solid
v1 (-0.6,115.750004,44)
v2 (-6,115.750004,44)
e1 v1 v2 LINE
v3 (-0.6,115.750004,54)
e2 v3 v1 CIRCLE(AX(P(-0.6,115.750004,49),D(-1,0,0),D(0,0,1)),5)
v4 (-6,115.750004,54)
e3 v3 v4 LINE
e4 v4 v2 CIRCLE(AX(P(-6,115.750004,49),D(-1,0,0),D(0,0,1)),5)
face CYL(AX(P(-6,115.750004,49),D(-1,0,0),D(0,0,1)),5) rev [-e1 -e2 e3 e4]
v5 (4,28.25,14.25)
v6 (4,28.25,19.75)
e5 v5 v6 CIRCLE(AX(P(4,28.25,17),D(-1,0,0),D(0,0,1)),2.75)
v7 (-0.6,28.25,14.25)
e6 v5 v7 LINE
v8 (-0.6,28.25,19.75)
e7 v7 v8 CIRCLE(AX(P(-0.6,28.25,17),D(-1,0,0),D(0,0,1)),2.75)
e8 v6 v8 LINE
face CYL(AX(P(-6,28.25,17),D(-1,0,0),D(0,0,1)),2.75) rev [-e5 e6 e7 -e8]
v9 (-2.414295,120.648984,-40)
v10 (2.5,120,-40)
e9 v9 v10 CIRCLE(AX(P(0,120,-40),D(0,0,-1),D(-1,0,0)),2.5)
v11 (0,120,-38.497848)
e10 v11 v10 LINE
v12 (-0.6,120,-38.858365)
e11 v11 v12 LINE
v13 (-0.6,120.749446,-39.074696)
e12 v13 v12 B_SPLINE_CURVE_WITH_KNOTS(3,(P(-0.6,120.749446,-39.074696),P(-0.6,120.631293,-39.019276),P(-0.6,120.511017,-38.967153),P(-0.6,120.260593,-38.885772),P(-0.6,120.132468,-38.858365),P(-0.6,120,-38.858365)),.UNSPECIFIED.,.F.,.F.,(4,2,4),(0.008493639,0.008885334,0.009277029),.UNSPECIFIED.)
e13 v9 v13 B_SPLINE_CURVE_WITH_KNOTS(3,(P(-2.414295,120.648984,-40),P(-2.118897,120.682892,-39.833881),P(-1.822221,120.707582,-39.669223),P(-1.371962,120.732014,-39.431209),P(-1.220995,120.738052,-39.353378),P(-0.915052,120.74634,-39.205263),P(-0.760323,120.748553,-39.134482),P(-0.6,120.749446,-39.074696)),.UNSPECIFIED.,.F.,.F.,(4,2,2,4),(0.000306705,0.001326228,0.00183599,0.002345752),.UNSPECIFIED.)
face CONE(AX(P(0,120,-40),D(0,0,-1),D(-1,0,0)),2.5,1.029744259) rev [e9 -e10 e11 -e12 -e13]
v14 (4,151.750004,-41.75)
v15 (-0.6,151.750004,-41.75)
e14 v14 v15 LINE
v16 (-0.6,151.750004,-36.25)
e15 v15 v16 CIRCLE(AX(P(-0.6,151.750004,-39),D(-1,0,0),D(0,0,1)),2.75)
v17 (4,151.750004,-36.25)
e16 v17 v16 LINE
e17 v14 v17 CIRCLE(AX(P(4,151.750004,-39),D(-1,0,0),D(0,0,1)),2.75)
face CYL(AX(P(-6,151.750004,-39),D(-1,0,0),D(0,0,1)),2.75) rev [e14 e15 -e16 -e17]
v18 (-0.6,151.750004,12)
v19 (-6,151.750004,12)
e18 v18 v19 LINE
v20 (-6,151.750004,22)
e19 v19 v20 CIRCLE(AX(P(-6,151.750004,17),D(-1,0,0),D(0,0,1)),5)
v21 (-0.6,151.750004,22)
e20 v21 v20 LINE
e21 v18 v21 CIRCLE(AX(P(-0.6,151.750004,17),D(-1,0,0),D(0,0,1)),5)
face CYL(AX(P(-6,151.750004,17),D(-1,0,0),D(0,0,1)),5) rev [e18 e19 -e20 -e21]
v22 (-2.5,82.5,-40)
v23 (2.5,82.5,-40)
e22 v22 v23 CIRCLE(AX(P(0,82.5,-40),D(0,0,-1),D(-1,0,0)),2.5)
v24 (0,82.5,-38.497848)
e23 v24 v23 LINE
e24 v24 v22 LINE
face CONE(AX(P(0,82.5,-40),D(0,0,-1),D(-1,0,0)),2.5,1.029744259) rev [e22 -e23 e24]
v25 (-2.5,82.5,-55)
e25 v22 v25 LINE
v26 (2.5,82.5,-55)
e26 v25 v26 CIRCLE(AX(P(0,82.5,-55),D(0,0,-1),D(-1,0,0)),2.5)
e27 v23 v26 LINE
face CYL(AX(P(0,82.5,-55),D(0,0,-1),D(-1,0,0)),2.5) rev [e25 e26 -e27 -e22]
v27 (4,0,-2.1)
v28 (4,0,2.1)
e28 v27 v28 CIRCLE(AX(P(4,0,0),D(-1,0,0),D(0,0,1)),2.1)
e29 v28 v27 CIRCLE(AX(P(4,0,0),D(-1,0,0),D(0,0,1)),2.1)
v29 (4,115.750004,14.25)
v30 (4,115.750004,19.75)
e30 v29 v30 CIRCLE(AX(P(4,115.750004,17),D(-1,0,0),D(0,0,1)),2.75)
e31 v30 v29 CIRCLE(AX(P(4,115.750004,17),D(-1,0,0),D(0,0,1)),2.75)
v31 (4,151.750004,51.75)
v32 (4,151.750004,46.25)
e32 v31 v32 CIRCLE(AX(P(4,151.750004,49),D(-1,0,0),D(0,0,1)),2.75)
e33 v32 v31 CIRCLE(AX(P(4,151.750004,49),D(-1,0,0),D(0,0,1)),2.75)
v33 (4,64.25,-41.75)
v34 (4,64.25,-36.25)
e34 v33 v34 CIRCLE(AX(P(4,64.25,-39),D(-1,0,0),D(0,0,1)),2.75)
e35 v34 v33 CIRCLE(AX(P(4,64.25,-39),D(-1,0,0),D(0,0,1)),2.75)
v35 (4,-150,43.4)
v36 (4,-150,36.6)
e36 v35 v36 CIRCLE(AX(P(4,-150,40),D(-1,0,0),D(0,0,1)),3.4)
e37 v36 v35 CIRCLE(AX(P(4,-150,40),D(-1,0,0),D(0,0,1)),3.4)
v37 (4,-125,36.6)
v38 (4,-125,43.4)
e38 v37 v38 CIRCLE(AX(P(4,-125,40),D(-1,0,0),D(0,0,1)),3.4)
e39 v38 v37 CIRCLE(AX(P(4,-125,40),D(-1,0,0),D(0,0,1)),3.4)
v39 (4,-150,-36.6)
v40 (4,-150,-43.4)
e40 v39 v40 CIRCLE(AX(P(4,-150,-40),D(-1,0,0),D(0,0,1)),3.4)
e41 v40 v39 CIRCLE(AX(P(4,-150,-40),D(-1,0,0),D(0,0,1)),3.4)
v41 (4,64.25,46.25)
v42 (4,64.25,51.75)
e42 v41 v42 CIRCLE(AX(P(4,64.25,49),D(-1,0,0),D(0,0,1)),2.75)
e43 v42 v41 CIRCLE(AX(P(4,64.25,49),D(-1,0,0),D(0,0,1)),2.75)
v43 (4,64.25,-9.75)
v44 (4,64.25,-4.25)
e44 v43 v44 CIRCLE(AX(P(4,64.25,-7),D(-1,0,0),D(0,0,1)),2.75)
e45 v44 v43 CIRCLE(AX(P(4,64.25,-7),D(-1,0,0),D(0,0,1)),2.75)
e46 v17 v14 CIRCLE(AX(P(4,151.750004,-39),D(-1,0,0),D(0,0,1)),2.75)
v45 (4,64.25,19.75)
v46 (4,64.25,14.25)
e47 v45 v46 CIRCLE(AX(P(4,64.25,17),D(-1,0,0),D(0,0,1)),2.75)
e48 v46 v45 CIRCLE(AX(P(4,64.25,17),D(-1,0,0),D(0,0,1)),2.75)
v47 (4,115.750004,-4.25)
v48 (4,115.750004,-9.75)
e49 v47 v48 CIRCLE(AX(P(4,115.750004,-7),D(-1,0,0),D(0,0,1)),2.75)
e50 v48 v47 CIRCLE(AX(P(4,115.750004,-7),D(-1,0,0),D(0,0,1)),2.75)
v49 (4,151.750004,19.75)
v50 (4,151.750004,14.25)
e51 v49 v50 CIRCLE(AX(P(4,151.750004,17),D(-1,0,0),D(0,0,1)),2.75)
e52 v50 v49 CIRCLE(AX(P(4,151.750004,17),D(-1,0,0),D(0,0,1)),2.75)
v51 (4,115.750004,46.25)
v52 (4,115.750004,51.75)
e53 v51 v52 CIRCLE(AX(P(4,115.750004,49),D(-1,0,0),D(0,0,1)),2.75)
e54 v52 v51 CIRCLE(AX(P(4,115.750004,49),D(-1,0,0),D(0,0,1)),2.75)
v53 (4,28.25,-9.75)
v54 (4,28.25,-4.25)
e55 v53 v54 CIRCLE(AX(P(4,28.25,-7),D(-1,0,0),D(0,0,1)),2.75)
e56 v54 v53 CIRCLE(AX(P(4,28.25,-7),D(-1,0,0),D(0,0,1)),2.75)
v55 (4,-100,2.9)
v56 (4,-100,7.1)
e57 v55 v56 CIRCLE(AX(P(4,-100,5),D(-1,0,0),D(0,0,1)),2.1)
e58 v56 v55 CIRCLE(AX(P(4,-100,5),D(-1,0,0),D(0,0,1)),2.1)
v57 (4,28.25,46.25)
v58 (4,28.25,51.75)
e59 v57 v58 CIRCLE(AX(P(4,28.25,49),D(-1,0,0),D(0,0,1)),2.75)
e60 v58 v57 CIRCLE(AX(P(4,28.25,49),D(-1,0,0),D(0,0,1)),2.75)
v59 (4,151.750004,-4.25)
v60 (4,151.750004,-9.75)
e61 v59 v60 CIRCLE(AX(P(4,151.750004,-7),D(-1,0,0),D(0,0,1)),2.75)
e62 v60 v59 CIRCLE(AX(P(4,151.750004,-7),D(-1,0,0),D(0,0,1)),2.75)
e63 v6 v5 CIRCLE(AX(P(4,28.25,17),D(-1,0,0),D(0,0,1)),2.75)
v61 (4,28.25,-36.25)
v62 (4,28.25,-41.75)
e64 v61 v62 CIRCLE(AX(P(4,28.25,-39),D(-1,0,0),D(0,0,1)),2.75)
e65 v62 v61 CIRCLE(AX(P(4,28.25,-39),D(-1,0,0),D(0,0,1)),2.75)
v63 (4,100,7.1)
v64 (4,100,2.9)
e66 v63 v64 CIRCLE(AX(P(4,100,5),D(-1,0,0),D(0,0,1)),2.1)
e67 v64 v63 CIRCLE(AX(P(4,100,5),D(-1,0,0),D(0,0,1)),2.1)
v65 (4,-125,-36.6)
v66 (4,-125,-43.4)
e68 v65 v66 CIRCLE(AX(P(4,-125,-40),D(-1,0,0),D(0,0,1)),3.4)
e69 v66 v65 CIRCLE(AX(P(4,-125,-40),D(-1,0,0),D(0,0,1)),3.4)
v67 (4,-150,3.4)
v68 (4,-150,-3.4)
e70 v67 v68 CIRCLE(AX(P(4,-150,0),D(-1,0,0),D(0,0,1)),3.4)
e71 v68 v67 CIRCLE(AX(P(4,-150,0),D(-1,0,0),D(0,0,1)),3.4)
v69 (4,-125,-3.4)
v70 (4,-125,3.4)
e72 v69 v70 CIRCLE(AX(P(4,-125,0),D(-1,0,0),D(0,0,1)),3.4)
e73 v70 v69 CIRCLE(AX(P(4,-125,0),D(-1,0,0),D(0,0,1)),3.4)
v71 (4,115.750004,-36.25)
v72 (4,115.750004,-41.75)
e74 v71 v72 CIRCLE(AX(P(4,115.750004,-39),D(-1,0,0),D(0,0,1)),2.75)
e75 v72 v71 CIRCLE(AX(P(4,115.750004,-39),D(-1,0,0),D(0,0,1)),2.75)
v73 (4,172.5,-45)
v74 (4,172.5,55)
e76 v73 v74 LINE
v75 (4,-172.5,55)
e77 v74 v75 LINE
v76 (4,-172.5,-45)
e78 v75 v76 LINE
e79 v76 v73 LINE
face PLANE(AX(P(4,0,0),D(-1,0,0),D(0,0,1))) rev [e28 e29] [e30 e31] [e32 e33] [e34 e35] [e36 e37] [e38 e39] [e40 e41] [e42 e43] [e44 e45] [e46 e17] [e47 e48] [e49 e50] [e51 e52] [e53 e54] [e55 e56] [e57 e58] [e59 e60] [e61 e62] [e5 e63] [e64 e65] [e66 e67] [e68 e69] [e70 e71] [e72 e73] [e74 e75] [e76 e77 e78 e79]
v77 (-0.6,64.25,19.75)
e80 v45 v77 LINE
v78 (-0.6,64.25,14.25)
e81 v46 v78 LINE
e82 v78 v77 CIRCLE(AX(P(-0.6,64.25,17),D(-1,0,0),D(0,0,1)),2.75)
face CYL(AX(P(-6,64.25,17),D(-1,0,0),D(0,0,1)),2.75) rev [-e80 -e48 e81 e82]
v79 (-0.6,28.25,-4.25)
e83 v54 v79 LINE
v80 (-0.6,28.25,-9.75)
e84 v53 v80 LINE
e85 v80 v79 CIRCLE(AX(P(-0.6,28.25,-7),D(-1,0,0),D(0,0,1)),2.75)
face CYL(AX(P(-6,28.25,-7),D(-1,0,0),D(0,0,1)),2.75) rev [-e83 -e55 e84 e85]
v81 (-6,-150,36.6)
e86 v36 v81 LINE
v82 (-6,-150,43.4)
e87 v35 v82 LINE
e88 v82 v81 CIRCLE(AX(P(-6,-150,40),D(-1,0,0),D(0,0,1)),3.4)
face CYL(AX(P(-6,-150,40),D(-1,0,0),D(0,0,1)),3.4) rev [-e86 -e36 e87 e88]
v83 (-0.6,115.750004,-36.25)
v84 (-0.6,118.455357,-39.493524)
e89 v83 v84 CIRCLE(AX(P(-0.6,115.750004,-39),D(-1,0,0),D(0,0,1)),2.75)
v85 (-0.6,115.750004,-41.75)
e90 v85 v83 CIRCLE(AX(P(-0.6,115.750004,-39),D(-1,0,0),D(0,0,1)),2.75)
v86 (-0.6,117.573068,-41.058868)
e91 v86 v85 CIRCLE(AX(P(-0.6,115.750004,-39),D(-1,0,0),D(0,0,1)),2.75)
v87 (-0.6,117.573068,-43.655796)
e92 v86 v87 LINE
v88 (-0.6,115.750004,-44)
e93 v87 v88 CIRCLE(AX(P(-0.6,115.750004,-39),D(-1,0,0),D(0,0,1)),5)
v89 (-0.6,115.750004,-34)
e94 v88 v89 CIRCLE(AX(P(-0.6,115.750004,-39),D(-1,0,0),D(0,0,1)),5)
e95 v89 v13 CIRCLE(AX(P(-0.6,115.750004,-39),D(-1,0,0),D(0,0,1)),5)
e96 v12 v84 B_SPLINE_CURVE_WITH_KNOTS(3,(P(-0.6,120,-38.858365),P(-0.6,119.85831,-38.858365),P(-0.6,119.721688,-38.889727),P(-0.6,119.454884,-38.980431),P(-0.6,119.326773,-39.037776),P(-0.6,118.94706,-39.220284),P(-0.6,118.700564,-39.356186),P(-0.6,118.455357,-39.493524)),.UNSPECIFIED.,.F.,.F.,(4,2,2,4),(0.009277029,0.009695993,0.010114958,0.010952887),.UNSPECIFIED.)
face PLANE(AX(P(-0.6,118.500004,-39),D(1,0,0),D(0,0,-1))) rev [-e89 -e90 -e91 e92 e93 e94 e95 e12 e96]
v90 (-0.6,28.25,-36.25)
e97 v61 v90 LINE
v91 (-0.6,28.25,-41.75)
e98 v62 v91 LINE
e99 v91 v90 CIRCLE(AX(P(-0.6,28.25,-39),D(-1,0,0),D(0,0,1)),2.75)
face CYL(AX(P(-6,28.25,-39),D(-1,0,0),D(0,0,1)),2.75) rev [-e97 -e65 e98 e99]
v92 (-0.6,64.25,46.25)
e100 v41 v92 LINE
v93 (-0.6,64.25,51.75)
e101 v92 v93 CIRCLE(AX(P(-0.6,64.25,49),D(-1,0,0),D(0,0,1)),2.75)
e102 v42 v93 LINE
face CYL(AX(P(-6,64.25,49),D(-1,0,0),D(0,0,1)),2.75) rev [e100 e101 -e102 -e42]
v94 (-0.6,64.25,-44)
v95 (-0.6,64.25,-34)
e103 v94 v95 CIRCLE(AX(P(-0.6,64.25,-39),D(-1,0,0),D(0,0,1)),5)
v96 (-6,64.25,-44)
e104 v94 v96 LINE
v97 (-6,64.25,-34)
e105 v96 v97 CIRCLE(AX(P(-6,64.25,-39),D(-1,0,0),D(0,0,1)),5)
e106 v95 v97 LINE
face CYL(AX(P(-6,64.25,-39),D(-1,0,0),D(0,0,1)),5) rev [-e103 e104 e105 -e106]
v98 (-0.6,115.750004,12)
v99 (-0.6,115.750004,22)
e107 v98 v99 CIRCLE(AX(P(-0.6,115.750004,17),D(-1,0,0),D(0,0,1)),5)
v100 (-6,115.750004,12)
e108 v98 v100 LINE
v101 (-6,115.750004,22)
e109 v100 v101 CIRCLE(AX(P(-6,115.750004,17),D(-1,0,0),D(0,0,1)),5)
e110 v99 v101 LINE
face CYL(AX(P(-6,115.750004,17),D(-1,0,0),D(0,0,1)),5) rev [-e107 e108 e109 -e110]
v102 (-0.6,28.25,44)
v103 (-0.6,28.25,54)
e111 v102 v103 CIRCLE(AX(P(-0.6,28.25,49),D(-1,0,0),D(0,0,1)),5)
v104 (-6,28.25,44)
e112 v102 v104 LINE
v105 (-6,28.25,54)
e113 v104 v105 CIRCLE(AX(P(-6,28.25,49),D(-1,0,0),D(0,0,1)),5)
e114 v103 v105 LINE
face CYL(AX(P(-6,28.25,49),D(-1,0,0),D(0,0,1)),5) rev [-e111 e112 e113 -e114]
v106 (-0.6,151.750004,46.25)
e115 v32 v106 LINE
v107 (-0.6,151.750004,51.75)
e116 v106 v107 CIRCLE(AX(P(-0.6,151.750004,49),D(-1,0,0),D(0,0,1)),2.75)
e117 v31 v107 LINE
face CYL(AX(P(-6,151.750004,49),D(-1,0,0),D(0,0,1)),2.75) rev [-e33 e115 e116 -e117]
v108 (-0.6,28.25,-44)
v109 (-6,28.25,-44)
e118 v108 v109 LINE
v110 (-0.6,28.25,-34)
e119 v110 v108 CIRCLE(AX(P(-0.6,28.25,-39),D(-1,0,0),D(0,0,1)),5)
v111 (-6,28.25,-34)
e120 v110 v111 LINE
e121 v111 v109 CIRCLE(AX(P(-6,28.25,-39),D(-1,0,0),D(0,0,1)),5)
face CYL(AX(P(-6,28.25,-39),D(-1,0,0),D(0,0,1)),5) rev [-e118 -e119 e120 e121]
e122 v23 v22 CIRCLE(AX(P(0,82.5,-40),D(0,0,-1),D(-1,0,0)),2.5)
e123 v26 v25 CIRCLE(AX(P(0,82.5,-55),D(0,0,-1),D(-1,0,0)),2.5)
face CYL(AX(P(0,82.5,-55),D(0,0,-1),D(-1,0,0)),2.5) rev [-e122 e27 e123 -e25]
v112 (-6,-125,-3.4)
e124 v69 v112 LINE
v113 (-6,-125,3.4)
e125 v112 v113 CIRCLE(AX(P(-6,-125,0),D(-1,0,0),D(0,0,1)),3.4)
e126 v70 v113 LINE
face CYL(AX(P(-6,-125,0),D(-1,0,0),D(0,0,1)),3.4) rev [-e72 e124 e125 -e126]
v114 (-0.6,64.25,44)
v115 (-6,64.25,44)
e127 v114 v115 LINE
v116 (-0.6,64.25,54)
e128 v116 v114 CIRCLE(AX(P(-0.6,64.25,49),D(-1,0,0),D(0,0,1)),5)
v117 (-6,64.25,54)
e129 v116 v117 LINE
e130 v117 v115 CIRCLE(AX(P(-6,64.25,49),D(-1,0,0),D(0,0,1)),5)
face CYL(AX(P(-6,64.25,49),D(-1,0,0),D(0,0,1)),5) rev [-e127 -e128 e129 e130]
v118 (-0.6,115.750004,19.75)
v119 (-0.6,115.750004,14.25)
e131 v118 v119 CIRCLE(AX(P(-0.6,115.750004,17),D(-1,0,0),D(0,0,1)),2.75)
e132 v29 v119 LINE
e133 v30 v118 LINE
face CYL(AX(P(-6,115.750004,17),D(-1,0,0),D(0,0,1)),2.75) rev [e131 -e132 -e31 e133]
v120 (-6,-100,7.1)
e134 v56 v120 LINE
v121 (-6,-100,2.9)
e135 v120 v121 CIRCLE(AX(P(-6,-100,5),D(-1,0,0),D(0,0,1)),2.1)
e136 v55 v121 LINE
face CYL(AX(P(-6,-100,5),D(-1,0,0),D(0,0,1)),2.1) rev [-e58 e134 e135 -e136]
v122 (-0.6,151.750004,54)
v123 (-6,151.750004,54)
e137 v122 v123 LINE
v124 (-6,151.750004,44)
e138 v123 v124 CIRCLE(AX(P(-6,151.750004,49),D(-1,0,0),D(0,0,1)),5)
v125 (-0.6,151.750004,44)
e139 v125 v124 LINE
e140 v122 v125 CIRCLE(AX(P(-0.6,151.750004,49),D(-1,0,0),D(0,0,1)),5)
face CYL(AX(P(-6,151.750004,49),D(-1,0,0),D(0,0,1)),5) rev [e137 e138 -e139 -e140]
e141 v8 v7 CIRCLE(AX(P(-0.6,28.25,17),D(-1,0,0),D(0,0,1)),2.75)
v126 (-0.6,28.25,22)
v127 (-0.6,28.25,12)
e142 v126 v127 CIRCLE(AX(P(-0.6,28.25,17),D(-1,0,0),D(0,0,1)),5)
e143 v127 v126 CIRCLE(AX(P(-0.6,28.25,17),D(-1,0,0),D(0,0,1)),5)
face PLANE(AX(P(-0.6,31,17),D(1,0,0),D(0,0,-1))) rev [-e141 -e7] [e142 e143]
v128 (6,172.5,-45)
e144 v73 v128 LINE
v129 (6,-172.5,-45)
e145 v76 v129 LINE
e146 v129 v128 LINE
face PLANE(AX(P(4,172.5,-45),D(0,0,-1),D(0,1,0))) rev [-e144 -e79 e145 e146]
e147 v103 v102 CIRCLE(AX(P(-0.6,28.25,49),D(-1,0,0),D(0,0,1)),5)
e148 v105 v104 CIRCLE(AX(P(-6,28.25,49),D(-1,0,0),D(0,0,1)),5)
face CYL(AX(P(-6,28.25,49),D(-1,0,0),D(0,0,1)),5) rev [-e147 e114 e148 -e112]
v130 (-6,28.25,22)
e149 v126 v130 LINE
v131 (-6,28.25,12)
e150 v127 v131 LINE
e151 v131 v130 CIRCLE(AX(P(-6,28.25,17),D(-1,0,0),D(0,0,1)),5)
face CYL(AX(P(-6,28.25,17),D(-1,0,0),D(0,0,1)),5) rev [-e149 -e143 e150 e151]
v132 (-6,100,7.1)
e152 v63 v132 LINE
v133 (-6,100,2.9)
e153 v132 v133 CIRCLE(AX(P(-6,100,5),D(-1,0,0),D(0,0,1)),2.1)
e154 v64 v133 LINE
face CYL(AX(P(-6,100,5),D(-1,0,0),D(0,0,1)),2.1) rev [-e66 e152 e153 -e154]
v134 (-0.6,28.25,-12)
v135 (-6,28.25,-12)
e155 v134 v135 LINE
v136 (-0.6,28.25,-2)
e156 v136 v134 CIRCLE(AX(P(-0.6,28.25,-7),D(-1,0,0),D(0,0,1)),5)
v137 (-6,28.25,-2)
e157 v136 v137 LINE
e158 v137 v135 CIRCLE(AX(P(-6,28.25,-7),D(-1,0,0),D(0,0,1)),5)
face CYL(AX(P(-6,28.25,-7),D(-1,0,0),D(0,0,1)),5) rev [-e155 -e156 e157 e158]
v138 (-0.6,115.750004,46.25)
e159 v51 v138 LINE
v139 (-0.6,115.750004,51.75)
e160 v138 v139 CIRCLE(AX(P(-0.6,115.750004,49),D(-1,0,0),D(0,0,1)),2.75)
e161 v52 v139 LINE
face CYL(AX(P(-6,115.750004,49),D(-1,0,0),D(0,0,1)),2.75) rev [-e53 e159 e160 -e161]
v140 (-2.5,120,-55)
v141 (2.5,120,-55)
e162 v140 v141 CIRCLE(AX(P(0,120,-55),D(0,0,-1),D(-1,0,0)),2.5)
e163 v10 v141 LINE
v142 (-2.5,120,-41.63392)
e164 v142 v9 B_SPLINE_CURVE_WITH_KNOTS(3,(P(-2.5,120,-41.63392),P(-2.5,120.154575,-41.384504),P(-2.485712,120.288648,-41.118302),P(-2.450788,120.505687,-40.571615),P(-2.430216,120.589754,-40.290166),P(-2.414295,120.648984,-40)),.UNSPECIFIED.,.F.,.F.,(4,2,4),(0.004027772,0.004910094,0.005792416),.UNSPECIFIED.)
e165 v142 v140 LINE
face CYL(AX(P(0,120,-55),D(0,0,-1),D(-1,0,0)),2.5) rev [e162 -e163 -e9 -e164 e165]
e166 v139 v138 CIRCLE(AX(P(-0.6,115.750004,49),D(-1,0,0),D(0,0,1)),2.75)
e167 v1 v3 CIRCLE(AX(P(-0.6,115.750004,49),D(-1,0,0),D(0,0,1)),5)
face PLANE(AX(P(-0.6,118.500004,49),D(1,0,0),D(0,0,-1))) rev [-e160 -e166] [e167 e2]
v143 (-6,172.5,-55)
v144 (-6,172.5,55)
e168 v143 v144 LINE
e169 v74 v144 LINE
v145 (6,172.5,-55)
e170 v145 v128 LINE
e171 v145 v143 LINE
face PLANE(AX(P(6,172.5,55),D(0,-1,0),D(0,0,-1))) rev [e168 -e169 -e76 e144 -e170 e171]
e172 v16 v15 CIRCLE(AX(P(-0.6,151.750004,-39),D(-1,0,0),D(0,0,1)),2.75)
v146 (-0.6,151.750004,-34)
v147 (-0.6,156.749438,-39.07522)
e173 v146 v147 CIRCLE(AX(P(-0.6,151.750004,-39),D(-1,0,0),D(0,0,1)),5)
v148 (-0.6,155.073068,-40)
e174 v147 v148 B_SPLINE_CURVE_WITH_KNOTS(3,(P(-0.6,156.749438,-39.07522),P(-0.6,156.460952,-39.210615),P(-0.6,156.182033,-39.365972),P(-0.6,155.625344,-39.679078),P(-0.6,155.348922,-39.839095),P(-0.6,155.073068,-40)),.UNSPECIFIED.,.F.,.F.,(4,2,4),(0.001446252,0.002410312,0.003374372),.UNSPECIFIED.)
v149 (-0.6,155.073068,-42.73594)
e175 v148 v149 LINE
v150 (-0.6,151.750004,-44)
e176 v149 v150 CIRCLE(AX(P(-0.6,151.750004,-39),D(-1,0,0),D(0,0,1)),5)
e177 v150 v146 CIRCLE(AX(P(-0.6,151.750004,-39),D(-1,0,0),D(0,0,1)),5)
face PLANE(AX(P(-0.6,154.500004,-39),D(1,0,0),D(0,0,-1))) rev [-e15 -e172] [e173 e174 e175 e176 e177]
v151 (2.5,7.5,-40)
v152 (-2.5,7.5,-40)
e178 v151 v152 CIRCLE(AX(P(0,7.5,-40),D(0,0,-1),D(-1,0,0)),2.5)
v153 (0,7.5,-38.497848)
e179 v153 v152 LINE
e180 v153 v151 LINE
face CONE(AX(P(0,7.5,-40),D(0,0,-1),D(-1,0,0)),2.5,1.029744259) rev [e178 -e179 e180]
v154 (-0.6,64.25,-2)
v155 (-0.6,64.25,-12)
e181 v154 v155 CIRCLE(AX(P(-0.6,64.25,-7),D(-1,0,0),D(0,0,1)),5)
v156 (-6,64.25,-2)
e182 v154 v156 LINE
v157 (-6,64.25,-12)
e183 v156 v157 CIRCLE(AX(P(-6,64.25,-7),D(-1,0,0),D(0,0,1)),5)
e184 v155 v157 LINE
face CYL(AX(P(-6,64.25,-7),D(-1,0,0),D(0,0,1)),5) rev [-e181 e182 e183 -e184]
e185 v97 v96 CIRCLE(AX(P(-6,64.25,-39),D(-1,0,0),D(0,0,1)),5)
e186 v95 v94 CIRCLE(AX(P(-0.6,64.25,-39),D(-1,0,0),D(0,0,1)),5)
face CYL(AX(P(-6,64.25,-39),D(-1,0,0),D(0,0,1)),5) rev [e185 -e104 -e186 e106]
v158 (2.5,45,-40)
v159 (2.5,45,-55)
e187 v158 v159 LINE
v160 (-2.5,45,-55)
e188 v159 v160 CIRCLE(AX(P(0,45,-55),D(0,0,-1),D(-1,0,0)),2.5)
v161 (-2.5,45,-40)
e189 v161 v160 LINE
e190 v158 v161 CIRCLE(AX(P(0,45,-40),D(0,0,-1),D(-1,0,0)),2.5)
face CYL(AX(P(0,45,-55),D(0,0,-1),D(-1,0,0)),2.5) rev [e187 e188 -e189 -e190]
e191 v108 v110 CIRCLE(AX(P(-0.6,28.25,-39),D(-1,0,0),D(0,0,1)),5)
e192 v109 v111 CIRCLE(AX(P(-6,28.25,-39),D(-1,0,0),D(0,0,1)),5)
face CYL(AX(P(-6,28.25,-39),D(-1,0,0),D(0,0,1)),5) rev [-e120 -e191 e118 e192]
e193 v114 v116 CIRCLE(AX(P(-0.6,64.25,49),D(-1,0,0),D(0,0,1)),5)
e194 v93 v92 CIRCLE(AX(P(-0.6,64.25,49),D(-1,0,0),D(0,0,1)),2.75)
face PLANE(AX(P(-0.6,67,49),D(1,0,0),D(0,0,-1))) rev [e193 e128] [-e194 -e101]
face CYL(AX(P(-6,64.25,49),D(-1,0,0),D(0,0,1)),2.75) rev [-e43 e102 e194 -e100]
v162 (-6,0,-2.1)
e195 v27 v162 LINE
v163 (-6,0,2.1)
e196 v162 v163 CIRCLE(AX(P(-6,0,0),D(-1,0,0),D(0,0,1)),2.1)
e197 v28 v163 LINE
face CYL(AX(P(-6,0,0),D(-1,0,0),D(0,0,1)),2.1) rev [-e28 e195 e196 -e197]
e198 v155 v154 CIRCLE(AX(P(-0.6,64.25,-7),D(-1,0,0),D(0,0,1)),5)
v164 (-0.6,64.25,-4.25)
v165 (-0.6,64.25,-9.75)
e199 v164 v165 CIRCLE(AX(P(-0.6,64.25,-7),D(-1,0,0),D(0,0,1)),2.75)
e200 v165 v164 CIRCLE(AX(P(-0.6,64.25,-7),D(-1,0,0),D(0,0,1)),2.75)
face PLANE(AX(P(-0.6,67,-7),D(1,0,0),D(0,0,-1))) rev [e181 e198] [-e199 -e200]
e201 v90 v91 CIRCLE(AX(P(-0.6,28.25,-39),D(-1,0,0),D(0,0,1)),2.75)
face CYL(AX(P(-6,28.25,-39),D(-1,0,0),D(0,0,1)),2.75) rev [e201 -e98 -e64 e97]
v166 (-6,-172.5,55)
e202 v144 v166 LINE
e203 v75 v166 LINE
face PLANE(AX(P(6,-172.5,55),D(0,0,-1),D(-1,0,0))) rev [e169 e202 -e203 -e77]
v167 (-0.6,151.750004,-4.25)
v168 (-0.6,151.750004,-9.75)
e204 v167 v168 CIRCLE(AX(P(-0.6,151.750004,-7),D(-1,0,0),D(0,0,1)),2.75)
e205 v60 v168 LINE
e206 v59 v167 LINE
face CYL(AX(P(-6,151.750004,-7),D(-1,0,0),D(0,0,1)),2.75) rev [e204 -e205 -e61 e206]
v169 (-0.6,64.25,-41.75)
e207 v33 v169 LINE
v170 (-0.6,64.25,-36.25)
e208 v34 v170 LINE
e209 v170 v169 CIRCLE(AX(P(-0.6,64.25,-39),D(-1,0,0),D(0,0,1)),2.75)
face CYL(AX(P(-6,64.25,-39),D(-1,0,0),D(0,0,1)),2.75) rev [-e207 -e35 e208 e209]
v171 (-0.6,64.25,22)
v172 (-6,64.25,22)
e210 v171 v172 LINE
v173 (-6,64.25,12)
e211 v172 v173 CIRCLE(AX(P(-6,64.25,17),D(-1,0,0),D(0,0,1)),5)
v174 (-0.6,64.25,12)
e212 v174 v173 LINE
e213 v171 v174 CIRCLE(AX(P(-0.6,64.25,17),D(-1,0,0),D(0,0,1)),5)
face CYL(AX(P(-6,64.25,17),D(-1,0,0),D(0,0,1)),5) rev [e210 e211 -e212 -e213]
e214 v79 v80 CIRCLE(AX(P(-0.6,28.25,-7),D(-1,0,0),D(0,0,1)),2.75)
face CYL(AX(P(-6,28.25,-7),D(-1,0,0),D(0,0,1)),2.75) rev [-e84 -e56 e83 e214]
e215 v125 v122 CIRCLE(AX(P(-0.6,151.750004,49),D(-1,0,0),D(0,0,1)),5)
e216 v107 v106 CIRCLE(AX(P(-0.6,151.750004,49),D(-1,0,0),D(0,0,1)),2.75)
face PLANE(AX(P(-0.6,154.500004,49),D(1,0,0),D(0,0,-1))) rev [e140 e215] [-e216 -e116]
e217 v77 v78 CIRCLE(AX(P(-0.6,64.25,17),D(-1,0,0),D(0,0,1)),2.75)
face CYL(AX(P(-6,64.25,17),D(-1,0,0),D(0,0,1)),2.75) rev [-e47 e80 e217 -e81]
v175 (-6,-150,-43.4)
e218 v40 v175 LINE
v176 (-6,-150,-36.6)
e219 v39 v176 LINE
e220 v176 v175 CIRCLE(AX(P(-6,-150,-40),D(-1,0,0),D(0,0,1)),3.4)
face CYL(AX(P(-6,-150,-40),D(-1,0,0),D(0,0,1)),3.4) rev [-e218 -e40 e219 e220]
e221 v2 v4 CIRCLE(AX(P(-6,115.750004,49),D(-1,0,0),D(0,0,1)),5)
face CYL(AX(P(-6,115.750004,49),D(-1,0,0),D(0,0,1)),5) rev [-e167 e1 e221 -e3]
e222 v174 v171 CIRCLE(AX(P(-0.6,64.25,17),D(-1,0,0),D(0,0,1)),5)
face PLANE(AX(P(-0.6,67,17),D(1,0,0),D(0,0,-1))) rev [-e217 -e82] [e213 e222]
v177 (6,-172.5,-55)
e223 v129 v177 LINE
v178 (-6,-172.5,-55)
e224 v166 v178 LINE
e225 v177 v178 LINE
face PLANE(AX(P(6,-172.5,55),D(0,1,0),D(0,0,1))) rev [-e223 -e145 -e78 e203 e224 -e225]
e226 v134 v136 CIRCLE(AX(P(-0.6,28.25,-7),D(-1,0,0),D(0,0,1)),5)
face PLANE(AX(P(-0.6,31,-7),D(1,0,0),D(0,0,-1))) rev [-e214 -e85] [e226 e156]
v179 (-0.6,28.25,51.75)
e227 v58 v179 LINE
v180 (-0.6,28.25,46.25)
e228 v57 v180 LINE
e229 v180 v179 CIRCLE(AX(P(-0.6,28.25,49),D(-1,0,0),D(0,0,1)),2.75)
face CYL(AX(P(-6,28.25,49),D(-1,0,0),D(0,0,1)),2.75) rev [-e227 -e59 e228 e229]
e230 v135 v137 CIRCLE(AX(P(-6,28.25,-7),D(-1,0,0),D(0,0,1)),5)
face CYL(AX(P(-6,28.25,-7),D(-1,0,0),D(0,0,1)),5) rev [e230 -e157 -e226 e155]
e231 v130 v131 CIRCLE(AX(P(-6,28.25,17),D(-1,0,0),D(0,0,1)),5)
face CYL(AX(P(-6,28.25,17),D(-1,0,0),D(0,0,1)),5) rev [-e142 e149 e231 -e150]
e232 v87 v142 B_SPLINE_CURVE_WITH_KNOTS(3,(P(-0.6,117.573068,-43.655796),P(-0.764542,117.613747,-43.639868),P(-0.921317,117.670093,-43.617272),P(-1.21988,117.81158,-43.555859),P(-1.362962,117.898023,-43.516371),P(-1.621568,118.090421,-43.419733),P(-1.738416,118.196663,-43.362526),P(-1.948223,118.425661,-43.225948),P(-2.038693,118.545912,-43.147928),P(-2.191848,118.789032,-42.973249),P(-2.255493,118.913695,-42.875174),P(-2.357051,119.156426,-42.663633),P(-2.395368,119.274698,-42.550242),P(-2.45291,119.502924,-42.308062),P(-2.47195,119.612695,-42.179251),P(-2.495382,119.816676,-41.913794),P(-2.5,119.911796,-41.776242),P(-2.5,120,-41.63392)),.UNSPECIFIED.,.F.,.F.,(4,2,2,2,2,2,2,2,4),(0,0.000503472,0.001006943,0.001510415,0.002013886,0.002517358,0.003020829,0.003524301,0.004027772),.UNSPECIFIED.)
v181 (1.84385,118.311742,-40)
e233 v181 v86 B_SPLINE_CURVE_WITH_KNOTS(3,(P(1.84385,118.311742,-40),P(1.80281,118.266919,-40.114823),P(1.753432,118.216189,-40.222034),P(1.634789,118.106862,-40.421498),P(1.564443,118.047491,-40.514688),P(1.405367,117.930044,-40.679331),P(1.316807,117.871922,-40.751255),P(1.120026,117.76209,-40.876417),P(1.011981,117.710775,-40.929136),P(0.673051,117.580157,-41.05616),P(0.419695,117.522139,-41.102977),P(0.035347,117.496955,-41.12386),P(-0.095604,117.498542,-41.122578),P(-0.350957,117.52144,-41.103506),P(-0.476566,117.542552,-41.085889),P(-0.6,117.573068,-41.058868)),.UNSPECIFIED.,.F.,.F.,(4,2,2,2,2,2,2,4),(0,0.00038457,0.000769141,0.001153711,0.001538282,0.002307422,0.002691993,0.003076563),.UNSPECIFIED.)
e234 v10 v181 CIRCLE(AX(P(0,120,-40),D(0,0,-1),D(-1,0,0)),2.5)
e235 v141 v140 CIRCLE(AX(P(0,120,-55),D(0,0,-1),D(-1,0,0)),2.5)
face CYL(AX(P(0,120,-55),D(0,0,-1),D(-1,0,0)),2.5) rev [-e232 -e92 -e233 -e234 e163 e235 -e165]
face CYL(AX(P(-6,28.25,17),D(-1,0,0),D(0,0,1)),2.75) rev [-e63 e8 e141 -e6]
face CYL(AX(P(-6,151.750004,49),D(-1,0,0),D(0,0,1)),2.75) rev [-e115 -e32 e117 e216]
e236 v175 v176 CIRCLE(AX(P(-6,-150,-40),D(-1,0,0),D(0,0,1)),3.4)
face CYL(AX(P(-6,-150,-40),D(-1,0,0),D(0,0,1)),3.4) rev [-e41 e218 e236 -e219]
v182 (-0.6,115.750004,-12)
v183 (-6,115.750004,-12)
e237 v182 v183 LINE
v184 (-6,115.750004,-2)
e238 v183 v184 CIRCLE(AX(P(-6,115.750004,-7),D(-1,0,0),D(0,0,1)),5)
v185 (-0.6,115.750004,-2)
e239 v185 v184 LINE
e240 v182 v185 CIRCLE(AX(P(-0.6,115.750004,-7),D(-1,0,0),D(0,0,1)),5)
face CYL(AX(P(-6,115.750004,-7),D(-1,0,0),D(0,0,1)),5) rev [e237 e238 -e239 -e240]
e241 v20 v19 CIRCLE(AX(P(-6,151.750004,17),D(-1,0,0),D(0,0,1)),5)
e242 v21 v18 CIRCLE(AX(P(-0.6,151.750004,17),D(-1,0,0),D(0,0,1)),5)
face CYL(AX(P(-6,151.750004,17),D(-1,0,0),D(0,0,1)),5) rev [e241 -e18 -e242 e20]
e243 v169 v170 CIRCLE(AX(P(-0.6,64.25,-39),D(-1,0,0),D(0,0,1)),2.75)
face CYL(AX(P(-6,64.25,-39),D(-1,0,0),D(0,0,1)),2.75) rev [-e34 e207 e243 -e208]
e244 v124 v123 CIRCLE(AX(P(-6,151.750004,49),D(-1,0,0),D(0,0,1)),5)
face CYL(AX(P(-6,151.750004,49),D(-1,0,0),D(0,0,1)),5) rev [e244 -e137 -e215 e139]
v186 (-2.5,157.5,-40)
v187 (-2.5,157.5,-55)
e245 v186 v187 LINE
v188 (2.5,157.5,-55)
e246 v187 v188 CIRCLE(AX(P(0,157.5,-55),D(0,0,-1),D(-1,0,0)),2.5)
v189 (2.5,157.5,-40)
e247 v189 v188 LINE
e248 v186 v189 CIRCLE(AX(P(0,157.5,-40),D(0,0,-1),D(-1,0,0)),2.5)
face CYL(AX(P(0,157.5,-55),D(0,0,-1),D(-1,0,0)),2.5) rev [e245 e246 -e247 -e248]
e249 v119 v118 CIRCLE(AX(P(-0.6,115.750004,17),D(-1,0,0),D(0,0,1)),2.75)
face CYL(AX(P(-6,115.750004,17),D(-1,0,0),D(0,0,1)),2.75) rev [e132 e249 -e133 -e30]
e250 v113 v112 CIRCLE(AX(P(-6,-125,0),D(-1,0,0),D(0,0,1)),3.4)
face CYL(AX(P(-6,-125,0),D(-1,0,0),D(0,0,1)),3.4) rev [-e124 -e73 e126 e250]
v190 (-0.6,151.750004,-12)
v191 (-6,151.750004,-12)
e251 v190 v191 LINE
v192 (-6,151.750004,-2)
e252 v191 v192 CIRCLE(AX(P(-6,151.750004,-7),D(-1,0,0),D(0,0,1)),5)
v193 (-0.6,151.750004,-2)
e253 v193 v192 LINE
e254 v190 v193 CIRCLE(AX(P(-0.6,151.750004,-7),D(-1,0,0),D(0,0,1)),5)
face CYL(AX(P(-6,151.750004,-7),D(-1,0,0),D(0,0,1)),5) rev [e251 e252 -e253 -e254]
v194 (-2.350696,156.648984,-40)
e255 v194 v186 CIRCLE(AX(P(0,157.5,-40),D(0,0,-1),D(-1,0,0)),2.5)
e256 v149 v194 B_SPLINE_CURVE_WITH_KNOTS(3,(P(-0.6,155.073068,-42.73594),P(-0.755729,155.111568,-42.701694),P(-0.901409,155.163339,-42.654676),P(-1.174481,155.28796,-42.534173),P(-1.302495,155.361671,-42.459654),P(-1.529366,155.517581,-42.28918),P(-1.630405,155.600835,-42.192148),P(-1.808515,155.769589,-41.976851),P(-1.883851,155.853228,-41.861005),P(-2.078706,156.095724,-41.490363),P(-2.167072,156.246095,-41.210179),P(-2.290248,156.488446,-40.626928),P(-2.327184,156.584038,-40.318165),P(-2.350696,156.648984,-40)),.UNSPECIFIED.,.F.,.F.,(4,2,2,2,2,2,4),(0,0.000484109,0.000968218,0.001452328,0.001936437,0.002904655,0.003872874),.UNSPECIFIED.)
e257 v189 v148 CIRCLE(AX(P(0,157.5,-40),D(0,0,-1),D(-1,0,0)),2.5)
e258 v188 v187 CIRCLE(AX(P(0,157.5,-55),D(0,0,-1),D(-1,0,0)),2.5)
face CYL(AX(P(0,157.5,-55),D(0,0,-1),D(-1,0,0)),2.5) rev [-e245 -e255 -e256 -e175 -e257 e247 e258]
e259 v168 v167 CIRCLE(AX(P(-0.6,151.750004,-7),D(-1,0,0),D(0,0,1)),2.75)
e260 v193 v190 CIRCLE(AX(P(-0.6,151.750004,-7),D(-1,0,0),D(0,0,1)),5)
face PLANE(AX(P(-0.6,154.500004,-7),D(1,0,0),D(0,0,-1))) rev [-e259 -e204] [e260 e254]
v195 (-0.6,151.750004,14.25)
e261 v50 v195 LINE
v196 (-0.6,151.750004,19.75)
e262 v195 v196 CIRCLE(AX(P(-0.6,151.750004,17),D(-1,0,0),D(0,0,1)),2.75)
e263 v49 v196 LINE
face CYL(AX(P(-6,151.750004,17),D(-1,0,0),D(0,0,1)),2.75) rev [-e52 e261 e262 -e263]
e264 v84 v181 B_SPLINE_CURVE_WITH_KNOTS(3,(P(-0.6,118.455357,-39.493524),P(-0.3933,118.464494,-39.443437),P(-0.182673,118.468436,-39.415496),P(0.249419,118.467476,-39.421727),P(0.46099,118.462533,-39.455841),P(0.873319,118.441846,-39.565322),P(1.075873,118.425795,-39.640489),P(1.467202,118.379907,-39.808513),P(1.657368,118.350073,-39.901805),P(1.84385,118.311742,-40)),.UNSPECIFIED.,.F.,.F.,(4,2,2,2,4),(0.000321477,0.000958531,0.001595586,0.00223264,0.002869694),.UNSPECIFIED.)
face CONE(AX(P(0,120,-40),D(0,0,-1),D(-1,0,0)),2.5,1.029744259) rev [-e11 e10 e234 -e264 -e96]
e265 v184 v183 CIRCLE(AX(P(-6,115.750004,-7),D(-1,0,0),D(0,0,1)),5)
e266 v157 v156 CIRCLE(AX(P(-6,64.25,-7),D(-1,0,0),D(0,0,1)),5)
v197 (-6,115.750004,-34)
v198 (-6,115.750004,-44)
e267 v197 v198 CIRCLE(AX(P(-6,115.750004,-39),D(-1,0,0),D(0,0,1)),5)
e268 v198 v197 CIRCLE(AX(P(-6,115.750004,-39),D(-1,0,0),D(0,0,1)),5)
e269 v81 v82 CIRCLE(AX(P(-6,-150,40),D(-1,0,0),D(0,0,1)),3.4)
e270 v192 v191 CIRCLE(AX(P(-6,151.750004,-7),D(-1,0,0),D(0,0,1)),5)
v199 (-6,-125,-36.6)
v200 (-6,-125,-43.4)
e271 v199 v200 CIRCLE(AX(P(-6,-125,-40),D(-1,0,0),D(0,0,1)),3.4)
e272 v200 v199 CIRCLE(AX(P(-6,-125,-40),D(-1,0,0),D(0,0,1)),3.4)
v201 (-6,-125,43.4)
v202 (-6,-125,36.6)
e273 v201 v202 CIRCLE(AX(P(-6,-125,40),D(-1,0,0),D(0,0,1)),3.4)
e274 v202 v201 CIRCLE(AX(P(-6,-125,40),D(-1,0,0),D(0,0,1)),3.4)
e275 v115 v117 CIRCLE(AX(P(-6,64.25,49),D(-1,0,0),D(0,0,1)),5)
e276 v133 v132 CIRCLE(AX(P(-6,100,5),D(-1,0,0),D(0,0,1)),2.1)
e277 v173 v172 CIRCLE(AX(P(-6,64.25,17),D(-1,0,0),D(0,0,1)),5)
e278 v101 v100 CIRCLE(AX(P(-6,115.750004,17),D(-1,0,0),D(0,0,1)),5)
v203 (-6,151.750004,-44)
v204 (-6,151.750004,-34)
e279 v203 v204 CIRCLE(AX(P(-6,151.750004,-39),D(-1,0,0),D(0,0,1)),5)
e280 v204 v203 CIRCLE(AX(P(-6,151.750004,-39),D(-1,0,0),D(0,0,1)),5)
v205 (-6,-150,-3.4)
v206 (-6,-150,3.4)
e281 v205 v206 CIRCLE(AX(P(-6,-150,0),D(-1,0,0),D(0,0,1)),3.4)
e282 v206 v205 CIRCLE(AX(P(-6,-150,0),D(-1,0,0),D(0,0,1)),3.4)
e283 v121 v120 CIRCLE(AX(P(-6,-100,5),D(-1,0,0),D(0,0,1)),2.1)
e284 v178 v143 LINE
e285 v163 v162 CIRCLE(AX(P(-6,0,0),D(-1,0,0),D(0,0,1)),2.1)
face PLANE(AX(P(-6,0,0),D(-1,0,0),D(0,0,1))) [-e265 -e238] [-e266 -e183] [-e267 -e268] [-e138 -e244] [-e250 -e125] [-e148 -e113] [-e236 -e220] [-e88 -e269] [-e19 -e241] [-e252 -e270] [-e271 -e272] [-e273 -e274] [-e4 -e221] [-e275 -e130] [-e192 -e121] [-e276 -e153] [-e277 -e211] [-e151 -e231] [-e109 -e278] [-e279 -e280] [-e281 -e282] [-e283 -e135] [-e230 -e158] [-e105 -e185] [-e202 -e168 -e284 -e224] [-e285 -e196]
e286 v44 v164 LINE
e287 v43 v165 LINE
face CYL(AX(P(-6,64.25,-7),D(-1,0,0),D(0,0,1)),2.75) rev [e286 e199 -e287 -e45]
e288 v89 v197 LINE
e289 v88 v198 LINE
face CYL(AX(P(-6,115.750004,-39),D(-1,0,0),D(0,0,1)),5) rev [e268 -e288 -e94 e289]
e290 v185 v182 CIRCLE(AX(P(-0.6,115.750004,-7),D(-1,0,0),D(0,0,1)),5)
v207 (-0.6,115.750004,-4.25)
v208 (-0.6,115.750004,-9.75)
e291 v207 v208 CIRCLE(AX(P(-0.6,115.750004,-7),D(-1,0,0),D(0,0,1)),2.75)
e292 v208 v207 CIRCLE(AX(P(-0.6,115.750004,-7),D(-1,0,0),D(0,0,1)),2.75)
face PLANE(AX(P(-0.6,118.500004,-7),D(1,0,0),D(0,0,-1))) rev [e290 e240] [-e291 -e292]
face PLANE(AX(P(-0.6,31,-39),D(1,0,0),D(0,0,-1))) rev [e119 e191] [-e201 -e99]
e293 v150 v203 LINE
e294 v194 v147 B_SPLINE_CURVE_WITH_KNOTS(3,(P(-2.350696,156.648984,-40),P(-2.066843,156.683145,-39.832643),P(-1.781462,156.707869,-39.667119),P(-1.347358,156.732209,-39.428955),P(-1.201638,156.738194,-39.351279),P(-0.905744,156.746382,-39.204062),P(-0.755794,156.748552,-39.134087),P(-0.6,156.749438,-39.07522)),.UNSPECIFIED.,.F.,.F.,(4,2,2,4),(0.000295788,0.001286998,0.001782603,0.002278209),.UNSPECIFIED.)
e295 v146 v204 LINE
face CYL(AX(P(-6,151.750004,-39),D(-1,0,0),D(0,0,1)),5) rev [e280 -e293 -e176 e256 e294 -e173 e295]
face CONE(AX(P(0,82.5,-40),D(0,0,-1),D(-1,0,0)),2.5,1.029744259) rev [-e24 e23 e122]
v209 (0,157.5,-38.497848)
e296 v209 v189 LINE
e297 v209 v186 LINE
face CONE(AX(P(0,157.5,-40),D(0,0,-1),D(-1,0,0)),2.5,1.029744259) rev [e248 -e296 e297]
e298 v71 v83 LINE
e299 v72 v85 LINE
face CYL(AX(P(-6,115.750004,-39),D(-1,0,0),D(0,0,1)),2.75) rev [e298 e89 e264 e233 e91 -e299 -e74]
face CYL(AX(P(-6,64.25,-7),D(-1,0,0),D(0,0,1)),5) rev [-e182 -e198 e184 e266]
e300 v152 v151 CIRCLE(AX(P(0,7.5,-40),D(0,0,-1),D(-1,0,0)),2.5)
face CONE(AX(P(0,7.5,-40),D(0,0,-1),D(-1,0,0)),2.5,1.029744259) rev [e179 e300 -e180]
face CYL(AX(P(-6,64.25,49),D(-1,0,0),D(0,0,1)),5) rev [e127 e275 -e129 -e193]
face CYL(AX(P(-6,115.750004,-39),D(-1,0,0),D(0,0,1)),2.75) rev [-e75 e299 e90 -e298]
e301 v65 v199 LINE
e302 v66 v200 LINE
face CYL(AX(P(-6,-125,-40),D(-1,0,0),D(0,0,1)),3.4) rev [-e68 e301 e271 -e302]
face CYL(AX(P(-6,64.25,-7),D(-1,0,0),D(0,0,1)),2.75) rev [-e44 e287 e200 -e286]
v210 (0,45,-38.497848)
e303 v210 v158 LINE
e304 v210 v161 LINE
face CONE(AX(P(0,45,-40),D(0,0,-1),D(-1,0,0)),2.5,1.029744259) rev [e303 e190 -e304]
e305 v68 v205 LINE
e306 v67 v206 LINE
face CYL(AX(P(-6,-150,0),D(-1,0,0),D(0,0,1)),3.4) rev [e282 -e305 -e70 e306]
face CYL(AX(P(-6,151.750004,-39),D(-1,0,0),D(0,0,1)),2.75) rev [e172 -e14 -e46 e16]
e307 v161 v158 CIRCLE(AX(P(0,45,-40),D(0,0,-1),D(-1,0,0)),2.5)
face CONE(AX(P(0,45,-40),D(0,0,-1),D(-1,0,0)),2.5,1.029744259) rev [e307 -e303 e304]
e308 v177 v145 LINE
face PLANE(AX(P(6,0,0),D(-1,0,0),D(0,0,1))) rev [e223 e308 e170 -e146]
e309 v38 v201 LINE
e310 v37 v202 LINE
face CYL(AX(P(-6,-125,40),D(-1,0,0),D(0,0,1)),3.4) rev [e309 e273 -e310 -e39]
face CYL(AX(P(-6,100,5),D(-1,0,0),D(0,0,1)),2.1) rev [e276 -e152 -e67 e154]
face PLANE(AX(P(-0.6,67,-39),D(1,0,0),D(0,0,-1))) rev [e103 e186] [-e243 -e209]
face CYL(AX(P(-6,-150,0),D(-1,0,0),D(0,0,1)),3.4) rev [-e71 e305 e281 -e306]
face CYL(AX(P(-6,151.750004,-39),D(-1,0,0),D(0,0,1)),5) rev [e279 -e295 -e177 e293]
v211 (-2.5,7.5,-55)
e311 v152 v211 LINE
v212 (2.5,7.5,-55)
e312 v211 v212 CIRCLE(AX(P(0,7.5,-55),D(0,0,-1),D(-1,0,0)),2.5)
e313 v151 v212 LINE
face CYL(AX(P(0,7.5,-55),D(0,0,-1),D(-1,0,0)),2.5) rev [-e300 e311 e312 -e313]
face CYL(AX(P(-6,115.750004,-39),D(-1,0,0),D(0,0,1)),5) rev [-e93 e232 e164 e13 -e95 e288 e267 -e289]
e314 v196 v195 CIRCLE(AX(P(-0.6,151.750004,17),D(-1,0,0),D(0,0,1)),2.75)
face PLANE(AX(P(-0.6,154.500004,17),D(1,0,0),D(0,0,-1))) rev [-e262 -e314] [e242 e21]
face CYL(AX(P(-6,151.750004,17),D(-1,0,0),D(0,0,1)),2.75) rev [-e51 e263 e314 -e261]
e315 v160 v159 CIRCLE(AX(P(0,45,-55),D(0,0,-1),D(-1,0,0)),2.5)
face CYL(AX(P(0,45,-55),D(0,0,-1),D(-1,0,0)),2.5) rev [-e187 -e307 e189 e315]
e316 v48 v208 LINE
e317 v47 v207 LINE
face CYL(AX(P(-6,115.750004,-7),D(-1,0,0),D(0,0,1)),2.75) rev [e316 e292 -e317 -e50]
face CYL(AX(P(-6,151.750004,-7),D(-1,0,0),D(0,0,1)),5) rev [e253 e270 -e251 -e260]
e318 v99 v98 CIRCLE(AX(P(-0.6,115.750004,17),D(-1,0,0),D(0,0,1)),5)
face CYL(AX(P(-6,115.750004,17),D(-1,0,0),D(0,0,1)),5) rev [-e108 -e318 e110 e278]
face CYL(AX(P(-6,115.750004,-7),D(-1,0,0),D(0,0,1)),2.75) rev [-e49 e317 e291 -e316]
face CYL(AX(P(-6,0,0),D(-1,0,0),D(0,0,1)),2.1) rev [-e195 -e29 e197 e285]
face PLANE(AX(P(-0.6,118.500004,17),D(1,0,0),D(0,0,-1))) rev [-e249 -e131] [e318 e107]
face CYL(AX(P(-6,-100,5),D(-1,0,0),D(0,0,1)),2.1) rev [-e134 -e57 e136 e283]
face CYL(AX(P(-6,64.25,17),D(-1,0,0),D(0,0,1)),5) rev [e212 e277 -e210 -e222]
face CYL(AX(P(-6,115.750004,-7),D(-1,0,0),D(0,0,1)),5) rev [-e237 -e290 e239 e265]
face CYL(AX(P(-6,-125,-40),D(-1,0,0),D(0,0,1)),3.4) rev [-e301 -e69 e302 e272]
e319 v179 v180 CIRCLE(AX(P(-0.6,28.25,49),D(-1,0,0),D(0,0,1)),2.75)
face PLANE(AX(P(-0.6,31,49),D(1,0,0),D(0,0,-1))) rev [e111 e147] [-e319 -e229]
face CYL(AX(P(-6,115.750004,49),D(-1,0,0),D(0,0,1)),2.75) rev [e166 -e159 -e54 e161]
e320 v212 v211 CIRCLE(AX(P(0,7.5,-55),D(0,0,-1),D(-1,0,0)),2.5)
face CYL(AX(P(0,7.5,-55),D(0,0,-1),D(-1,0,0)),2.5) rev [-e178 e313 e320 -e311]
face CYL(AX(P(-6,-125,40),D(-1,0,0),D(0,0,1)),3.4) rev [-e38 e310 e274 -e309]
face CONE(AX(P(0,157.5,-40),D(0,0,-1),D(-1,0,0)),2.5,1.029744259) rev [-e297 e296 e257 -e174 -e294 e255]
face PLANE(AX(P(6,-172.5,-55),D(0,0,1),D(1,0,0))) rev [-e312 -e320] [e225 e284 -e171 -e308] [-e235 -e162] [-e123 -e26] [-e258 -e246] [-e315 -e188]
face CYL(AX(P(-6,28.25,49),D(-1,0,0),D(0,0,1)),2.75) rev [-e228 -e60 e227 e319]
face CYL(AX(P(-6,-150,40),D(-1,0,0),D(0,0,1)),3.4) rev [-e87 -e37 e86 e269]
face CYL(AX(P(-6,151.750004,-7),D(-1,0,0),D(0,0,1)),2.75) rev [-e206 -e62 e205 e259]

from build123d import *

# Parameters (mm, degrees)
SKETCH_1_W                   = 110
SKETCH_1_H                   = 345
EXTRUDE_1_DEPTH              = 6
SKETCH_2_W                   = 100
SKETCH_2_H                   = 345
CUT_EXTRUDE_1_DEPTH          = 2
HOLE_WIZARD_M5_1_D           = 5.5
HOLE_WIZARD_M5_1_CBORE_D     = 10
HOLE_WIZARD_M5_1_CBORE_DEPTH = 5.4
HOLE_WIZARD_M8_1_D           = 6.8
HOLE_WIZARD_M5_1_2_D         = 4.2
HOLE_WIZARD_M6_1_D           = 5
HOLE_WIZARD_M6_1_DEPTH       = 15
HOLE_WIZARD_M6_1_TIP         = 1.502151548


with BuildPart() as part:
    # 草图1 → 凸台-拉伸1 (new, symmetric)
    with BuildSketch(Plane(origin=(0, 0, 0), x_dir=(0, 0, -1), z_dir=(1, 0, 0))):
        Rectangle(SKETCH_1_W, SKETCH_1_H)
    extrude(amount=EXTRUDE_1_DEPTH, both=True)

    # 草图2 → 切除-拉伸1 (cut)
    with BuildSketch(Plane(origin=(6, 0, 0), x_dir=(0, 0, -1), z_dir=(1, 0, 0))):
        with Locations((-5, 0)):
            Rectangle(SKETCH_2_W, SKETCH_2_H)
    extrude(amount=-CUT_EXTRUDE_1_DEPTH, mode=Mode.SUBTRACT)

    # Hole Wizard M5 _1 (through all)
    with Locations(Plane.ZY.offset(6)):
        with Locations((-39, 151.75000402), (-7, 151.75000402), (17, 151.75000402), (49, 151.75000402), (49, 115.75000402), (17, 115.75000402), (-7, 115.75000402), (-39, 115.75000402), (-39, 64.250000001), (-7, 64.250000001), (17, 64.250000001), (49, 64.250000001), (-39, 28.250000001), (-7, 28.250000001), (17, 28.250000001), (49, 28.250000001)):
            CounterBoreHole(HOLE_WIZARD_M5_1_D / 2, HOLE_WIZARD_M5_1_CBORE_D / 2, HOLE_WIZARD_M5_1_CBORE_DEPTH)

    # M8 螺纹孔1 (through all)
    with Locations(Plane.ZY.offset(6)):
        with Locations((-40, -125), (-40, -150), (0, -125), (0, -150), (40, -125), (40, -150)):
            Hole(HOLE_WIZARD_M8_1_D / 2)

    # Hole Wizard M5 _1 2 (through all)
    with Locations(Plane.ZY.offset(6)):
        with Locations((0, 0), (5, 100), (5, 185), (5, -100)):
            Hole(HOLE_WIZARD_M5_1_2_D / 2)

    # M6 螺纹孔1
    with Locations(Plane(origin=(0, 0, -55), x_dir=(-1, 0, 0), z_dir=(0, 0, -1))):
        with Locations((0, 157.5), (0, 120), (0, 82.5), (0, 45), (0, 7.5)):
            Hole(HOLE_WIZARD_M6_1_D / 2, depth=HOLE_WIZARD_M6_1_DEPTH)
            with Locations((0, 0, -(HOLE_WIZARD_M6_1_DEPTH + HOLE_WIZARD_M6_1_TIP / 2))):  # 118° drill point
                Cone(0, HOLE_WIZARD_M6_1_D / 2, HOLE_WIZARD_M6_1_TIP, mode=Mode.SUBTRACT)


solid = part.part
